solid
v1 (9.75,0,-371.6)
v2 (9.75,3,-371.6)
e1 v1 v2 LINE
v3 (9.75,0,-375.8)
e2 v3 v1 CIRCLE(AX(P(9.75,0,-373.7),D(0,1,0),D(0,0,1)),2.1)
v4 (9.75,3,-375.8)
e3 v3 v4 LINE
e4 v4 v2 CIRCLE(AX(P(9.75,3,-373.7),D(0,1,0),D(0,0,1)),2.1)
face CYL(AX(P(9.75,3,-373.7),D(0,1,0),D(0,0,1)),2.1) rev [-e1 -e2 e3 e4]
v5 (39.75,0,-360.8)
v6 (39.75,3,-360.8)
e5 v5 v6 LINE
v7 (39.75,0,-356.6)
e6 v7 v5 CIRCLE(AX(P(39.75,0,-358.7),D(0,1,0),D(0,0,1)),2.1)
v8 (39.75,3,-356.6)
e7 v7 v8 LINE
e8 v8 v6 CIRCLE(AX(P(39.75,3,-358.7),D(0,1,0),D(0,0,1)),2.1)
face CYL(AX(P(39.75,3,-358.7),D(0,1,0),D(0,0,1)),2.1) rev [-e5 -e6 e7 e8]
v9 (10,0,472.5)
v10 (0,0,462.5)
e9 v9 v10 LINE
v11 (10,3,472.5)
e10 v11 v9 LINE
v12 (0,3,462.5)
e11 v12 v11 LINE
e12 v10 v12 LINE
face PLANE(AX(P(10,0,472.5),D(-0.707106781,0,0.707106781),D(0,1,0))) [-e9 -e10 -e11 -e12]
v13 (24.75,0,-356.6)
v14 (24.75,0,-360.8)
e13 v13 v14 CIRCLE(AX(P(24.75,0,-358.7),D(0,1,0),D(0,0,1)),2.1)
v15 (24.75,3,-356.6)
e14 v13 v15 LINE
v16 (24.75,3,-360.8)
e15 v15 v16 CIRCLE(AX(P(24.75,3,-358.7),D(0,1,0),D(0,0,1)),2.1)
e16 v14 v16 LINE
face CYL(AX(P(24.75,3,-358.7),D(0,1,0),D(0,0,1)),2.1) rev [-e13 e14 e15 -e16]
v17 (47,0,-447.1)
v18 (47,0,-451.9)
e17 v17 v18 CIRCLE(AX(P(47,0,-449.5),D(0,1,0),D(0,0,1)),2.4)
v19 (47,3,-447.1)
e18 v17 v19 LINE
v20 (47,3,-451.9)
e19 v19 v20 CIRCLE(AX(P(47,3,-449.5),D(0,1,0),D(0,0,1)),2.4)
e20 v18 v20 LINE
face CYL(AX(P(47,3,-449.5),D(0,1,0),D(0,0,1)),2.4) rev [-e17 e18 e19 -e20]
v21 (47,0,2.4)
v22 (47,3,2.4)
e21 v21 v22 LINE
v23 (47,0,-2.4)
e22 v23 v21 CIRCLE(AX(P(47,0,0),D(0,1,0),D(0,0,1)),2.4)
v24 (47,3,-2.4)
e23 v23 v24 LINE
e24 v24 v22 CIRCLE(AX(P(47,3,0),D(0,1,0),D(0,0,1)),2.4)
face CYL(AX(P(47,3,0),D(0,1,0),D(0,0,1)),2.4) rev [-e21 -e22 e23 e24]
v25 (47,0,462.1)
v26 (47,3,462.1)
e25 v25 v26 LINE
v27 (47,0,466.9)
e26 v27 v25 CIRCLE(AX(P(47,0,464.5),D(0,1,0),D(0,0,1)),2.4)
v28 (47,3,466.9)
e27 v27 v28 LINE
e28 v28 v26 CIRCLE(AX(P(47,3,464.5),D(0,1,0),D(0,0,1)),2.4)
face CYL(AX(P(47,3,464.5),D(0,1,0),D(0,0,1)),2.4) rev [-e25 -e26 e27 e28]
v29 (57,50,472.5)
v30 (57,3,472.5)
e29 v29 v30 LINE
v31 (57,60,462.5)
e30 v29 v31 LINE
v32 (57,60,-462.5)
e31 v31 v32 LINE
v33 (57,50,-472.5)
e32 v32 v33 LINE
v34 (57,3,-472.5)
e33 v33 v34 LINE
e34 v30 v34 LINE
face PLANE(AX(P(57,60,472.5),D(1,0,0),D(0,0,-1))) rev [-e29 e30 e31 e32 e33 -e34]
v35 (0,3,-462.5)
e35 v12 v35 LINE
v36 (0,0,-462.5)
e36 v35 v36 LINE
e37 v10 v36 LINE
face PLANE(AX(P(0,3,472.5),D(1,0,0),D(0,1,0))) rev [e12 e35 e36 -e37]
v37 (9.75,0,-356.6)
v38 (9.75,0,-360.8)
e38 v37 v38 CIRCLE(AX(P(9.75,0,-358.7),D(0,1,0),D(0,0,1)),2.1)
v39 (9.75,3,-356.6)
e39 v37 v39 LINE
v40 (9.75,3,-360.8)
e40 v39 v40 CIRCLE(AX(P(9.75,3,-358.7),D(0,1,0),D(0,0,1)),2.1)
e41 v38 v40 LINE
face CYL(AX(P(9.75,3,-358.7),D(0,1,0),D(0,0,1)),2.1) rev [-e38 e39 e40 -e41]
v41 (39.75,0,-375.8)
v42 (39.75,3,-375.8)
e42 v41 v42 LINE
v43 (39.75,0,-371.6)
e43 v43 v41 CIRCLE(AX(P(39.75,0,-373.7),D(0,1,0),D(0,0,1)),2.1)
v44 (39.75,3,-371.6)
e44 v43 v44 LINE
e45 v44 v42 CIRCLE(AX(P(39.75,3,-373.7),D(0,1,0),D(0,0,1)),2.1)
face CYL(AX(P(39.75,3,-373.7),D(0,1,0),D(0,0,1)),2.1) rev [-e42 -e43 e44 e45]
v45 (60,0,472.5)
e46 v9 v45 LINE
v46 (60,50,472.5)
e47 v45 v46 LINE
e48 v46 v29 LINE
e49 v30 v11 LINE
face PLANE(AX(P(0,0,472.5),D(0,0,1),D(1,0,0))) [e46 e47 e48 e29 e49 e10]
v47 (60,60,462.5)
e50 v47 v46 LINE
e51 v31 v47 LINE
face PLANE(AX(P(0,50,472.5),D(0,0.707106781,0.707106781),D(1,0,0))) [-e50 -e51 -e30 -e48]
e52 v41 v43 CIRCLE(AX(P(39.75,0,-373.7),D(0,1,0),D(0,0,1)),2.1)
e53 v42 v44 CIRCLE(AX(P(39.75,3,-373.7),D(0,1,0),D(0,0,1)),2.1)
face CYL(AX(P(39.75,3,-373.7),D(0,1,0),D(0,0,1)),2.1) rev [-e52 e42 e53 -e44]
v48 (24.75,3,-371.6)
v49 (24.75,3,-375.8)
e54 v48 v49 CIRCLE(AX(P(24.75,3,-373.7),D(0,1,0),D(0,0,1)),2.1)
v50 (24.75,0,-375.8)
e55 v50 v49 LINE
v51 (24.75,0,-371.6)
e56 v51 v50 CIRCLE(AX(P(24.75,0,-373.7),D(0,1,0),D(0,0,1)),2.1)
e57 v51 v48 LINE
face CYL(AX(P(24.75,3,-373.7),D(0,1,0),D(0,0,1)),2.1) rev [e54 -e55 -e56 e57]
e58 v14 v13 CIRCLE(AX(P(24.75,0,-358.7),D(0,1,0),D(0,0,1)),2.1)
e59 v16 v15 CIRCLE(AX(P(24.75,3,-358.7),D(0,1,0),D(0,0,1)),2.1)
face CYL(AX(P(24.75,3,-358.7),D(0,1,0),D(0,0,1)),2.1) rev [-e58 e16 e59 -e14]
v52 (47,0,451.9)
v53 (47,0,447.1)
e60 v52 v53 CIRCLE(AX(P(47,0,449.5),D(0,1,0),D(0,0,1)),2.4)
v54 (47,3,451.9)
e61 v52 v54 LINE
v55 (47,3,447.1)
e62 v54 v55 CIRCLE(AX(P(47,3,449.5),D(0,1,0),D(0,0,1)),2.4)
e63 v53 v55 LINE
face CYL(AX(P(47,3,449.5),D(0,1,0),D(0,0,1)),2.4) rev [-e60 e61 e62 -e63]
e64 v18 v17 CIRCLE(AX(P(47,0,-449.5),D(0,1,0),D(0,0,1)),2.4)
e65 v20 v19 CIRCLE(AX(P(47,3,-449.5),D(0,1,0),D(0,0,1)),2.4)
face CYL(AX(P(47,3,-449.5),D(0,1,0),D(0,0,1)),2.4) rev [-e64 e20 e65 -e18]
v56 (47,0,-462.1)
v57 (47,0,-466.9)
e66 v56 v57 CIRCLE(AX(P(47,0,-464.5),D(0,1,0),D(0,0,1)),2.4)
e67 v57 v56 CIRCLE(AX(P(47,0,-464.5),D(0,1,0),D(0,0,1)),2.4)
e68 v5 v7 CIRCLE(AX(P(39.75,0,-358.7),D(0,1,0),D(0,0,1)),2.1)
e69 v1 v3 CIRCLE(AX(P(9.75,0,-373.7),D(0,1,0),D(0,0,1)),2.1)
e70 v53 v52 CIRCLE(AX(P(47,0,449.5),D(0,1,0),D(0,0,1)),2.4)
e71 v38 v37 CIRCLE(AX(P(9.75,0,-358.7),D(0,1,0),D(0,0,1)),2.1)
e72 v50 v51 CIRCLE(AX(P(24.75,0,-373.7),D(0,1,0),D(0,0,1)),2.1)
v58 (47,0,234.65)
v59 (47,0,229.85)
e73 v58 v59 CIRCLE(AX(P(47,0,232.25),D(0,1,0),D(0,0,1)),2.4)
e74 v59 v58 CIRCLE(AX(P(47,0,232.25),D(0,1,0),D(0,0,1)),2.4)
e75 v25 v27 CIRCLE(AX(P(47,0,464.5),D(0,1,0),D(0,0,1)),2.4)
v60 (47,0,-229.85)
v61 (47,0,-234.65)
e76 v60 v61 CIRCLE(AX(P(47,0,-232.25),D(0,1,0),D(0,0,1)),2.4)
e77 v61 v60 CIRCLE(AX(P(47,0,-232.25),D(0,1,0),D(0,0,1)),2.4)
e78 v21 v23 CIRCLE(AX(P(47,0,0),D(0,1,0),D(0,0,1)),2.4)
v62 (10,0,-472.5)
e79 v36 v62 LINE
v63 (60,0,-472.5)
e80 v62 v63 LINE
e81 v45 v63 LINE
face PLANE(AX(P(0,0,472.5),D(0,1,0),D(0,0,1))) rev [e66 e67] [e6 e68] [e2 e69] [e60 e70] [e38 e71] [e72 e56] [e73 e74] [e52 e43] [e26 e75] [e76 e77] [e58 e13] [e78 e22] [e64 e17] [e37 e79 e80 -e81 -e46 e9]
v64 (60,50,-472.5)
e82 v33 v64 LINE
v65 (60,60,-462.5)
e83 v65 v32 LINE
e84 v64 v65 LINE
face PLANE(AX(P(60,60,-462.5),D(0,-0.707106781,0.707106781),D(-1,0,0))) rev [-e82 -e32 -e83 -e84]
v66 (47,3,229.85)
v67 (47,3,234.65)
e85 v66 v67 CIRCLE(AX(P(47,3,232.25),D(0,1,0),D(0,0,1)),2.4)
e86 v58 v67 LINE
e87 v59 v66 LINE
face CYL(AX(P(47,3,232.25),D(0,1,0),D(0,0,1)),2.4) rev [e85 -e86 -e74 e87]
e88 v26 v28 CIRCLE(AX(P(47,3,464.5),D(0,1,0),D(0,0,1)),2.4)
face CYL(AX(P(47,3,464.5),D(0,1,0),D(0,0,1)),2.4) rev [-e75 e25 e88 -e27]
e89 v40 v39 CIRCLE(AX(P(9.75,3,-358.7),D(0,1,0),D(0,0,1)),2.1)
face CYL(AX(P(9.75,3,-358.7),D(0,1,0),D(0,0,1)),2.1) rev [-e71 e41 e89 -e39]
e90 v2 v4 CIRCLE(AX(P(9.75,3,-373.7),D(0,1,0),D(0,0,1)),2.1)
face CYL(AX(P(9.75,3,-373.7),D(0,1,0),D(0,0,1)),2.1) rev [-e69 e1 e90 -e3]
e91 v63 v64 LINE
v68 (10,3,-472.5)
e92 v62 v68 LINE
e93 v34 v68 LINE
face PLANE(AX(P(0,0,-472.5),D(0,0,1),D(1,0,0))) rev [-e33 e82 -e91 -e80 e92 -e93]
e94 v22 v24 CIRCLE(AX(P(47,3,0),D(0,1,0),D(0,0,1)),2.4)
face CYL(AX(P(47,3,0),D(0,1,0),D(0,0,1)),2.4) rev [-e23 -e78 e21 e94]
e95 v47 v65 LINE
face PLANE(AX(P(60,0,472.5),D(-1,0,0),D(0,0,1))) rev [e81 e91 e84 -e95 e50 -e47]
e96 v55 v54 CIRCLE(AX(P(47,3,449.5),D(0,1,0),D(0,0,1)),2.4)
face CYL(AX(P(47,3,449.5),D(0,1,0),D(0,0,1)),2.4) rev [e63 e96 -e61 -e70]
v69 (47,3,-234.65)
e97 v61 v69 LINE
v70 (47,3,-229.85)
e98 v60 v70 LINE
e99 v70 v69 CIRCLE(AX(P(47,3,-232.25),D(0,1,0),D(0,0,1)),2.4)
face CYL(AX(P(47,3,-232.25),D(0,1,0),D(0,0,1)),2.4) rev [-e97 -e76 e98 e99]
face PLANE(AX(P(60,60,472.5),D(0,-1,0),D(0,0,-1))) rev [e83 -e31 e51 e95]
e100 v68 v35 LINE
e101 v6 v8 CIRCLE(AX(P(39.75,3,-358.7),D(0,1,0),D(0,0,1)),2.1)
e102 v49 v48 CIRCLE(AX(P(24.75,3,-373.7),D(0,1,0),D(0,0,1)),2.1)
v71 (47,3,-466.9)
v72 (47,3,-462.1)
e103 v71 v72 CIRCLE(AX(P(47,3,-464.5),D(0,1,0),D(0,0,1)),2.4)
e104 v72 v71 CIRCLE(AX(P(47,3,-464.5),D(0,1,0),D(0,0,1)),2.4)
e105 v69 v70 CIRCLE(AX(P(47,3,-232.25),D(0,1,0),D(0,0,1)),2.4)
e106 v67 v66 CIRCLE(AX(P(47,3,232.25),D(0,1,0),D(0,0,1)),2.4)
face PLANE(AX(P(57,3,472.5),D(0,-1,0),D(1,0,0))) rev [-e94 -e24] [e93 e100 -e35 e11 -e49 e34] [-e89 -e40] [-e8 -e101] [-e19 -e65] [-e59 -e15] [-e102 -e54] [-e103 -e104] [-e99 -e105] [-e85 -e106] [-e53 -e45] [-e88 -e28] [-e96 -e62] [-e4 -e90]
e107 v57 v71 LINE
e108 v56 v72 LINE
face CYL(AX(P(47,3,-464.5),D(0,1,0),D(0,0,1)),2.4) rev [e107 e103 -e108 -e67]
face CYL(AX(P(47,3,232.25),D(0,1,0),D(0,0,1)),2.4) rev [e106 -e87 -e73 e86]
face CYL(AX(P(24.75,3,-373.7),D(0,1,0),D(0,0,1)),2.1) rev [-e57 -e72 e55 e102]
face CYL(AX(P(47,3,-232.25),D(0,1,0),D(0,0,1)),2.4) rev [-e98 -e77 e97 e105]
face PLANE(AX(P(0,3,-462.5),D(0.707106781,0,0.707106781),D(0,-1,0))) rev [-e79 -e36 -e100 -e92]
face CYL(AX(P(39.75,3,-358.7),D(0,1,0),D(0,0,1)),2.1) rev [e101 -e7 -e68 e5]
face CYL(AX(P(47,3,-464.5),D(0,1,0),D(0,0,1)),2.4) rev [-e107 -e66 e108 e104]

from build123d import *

# Parameters (mm, degrees)
EXTRUDE_1_DEPTH    = 472.5
HOLE_WIZARD_M4_1_D = 4.8
CHAMFER_1_SIZE     = 10
HOLE_WIZARD_M5_1_D = 4.2


with BuildPart() as part:
    # 草图1 → 凸台-拉伸1 (new, symmetric)
    with BuildSketch(Plane.XY):
        Polygon((0, 0), (60, 0), (60, 60), (57, 60), (57, 3), (0, 3), align=None)
    extrude(amount=EXTRUDE_1_DEPTH, both=True)

    # M4 间隙孔1 (through all)
    with Locations(Plane(origin=(0, 3, 0), x_dir=(1, 0, 0), z_dir=(0, 1, 0))):
        with Locations((47, 0), (47, 232.25), (47, 464.5), (47, -464.5), (47, -232.25), (47, 449.5), (47, -449.5)):
            Hole(HOLE_WIZARD_M4_1_D / 2)

    # 倒角1
    chamfer_1_edges = [part.edges().sort_by_distance(p)[0] for p in [
        (58.5, 60, 472.5),
        (0, 1.5, 472.5),
        (58.5, 60, -472.5),
        (0, 1.5, -472.5),
    ]]
    chamfer(chamfer_1_edges, length=CHAMFER_1_SIZE)

    # M5 螺纹孔1 (through all)
    with Locations(Plane(origin=(0, 3, 0), x_dir=(1, 0, 0), z_dir=(0, 1, 0))):
        with Locations((9.75, 373.7), (39.75, 373.7), (24.75, 358.7), (9.75, 358.7), (39.75, 358.7), (24.75, 373.7)):
            Hole(HOLE_WIZARD_M5_1_D / 2)


solid = part.part
